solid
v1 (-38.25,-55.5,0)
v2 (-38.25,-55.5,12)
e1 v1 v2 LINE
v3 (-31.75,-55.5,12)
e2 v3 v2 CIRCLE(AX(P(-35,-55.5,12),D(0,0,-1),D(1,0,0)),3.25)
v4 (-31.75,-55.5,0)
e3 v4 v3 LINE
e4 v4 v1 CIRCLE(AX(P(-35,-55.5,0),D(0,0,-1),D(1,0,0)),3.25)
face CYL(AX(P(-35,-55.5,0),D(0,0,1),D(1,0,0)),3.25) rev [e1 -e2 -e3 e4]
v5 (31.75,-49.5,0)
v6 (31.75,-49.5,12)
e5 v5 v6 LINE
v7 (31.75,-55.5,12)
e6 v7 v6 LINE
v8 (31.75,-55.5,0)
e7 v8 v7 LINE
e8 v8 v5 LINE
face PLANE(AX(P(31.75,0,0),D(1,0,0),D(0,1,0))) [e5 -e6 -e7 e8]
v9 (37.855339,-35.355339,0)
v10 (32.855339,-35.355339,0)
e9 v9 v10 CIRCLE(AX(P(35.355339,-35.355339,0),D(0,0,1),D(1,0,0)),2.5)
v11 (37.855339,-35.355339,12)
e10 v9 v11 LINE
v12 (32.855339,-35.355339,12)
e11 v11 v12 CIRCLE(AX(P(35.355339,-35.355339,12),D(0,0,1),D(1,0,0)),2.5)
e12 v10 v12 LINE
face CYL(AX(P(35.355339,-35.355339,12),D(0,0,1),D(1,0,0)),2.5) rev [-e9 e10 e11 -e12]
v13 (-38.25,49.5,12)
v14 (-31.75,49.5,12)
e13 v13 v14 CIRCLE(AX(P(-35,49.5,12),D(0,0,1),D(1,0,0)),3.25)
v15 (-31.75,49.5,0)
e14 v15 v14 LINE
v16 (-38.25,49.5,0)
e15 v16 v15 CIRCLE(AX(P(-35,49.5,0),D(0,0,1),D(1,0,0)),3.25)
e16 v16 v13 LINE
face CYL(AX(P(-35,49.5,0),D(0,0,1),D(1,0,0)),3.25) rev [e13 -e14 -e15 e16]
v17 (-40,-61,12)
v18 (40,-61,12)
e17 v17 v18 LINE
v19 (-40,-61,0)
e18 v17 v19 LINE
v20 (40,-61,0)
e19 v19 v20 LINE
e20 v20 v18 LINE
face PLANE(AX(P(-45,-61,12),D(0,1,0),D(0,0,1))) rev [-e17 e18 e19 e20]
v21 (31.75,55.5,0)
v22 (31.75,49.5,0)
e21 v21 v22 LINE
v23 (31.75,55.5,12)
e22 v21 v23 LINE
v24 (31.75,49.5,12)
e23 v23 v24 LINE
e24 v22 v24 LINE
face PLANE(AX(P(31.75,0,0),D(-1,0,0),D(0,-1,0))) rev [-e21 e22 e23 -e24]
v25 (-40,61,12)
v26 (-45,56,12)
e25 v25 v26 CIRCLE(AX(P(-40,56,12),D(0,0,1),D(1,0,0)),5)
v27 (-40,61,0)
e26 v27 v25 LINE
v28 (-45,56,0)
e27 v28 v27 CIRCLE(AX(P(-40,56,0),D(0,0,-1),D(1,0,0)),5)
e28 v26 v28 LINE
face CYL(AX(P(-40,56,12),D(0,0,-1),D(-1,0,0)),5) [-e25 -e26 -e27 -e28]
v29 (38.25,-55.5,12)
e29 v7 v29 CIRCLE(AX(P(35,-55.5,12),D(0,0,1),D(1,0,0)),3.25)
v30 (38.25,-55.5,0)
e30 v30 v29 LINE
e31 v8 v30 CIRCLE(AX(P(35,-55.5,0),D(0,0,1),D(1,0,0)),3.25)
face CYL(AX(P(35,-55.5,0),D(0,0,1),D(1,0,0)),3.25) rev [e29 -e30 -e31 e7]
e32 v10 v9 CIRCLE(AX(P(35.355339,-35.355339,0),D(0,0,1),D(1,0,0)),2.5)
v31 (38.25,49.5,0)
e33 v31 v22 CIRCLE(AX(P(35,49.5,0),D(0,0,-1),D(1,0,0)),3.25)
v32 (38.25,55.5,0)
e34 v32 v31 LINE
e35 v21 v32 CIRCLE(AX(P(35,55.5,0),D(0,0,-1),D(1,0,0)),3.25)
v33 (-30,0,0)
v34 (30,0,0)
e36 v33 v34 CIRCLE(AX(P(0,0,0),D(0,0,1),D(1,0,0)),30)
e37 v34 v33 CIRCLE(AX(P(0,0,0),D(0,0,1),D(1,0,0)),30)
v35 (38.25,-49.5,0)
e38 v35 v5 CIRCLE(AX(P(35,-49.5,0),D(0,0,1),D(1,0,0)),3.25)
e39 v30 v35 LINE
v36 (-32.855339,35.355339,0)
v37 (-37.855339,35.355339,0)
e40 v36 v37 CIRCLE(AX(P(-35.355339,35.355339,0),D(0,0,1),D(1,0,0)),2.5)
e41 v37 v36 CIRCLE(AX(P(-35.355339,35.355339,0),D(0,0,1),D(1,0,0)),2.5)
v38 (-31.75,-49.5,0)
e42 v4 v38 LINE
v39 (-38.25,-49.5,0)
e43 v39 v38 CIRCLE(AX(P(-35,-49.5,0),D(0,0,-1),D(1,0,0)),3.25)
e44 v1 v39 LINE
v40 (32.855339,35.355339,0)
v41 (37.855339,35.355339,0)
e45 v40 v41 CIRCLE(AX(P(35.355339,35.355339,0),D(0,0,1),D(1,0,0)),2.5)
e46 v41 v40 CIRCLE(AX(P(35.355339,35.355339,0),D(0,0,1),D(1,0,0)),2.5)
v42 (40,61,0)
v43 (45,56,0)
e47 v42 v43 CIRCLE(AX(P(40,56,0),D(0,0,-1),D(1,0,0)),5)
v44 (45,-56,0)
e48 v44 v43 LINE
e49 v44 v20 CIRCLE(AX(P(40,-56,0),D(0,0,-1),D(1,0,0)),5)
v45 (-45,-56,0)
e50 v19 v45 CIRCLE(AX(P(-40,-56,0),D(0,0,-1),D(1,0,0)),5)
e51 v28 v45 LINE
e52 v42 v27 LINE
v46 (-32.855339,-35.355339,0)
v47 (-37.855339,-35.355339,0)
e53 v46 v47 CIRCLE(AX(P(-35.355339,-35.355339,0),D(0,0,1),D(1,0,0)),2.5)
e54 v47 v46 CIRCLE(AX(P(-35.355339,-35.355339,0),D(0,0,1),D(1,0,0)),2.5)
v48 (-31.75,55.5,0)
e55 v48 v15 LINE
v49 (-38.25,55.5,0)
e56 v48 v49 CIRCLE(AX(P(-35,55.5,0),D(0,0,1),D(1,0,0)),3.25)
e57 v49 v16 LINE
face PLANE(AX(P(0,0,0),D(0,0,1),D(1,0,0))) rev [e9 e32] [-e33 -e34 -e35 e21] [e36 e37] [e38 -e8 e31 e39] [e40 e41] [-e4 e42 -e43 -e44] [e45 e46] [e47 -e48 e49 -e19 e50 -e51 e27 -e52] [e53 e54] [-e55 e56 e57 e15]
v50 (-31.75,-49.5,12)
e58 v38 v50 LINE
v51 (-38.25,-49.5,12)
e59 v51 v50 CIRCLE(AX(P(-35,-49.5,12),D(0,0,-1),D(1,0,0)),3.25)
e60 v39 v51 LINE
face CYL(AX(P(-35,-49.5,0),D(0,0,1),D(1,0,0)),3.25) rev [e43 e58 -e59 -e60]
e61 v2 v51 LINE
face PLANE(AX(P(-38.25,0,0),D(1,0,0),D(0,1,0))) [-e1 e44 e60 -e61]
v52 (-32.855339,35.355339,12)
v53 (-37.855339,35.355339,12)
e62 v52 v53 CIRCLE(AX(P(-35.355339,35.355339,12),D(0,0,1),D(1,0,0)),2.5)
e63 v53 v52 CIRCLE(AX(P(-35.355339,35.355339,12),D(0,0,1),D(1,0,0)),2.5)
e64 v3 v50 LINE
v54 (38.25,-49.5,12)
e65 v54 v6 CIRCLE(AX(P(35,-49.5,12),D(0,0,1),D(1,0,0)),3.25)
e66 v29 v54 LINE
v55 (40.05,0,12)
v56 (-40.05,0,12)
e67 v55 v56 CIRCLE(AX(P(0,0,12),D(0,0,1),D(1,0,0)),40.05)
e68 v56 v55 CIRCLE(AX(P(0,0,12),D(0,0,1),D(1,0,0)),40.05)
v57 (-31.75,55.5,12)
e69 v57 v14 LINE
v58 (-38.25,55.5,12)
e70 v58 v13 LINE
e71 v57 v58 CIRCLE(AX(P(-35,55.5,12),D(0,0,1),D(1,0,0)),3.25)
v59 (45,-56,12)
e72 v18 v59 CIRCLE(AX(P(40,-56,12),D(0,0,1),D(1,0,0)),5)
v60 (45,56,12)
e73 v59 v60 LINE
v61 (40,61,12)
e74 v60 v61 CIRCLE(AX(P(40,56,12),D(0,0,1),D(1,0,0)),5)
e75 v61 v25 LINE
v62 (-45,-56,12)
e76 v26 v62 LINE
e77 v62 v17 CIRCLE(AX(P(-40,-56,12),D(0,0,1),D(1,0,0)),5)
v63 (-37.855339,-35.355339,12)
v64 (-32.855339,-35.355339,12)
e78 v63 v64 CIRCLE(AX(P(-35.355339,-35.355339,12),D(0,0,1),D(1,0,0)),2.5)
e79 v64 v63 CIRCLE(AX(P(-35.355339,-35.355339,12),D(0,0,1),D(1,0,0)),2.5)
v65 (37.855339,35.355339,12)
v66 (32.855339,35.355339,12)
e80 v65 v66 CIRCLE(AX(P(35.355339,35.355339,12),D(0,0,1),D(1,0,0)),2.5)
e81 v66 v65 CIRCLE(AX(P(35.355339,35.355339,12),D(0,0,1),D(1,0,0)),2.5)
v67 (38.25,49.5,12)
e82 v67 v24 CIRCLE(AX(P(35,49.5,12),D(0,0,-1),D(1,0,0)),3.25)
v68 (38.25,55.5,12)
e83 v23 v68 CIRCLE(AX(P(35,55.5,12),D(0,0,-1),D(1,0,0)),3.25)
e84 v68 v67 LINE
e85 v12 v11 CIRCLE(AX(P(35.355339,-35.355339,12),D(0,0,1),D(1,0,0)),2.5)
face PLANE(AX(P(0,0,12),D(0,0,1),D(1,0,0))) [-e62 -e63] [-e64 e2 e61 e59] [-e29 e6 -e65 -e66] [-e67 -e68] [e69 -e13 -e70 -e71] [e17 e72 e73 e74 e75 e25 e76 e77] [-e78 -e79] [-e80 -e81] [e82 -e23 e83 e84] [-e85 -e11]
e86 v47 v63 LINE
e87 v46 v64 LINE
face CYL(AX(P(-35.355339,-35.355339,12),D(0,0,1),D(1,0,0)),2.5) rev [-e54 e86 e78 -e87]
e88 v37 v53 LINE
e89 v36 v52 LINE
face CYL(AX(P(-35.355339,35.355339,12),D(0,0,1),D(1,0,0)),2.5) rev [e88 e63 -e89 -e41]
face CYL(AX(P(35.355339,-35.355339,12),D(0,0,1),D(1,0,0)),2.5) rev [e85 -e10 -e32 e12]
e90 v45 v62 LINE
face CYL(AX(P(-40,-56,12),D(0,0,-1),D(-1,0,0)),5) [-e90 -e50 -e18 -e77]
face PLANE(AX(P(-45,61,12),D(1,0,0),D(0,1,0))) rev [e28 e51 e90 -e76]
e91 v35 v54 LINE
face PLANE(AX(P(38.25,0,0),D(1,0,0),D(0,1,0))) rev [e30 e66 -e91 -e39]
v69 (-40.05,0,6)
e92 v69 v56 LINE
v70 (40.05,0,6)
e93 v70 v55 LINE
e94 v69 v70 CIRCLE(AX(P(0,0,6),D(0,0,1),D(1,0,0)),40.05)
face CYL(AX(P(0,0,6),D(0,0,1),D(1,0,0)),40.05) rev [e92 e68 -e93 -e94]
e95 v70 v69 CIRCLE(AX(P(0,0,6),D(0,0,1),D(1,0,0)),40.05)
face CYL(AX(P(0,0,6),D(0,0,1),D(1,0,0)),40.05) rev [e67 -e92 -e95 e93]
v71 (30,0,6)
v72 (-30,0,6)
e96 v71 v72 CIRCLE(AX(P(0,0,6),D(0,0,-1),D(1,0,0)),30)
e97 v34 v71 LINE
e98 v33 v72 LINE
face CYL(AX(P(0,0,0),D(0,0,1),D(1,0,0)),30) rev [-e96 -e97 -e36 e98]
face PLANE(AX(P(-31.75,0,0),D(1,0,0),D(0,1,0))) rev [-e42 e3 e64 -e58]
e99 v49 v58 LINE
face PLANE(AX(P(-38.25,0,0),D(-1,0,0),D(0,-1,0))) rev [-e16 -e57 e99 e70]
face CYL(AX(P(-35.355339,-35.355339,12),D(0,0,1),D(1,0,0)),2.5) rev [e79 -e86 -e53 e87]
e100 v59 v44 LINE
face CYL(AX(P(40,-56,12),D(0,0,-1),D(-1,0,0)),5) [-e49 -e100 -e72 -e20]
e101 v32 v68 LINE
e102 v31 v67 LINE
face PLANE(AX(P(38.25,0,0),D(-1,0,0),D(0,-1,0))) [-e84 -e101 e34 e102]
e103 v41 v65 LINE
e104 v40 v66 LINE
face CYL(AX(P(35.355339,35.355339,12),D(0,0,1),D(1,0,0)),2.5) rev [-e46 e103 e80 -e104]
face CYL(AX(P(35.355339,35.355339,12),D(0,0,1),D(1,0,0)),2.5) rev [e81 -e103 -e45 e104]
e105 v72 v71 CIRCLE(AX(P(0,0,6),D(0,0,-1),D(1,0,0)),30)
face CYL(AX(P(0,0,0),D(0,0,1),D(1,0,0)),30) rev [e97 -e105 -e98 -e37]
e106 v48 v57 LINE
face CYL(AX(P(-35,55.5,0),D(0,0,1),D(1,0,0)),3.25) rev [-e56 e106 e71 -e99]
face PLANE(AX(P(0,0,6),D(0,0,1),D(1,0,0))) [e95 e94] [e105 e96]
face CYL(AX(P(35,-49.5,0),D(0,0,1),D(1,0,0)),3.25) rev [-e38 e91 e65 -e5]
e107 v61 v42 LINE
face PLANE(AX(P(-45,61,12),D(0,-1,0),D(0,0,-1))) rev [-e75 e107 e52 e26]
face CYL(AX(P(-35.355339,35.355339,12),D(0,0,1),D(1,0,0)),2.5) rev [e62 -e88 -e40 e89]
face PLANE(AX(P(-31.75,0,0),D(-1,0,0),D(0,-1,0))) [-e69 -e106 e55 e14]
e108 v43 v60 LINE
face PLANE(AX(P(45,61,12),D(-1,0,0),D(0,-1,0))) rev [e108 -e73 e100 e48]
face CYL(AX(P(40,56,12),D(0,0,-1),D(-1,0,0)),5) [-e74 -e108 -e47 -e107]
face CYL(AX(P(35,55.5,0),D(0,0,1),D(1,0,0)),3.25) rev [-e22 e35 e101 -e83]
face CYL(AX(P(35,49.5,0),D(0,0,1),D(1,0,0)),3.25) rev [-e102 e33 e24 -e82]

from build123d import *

# Parameters (mm, degrees)
SKETCH1_W           = 90
SKETCH1_H           = 122
BOSS_EXTRUDE1_DEPTH = 12
SKETCH2_R           = 30
CUT_EXTRUDE1_DEPTH  = 77.746335417
SKETCH3_R           = 40.05
CUT_EXTRUDE2_DEPTH  = 6
M6_TAPPED_HOLE1_D   = 5
CUT_EXTRUDE3_DEPTH  = 77.746335417
FILLET1_R           = 5


with BuildPart() as part:
    # Sketch1 → Boss-Extrude1 (new body)
    with BuildSketch(Plane.XY):
        Rectangle(SKETCH1_W, SKETCH1_H)
    extrude(amount=BOSS_EXTRUDE1_DEPTH)

    # Sketch2 → Cut-Extrude1 (cut, through all)
    with BuildSketch(Plane.XY.offset(12)):
        Circle(SKETCH2_R)
    extrude(amount=-CUT_EXTRUDE1_DEPTH, mode=Mode.SUBTRACT)

    # Sketch3 → Cut-Extrude2 (cut)
    with BuildSketch(Plane.XY.offset(12)):
        Circle(SKETCH3_R)
    extrude(amount=-CUT_EXTRUDE2_DEPTH, mode=Mode.SUBTRACT)

    # M6 Tapped Hole1 (through all)
    with Locations(Plane.XY.offset(12)):
        with Locations((35.355339059, 35.355339059), (-35.355339059, 35.355339059), (-35.355339059, -35.355339059), (35.355339059, -35.355339059)):
            Hole(M6_TAPPED_HOLE1_D / 2)

    # Sketch6 → Cut-Extrude3 (cut, through all)
    with BuildSketch(Plane.XY.offset(12)):
        with BuildLine():
            Line((-38.25, 55.5), (-38.25, 49.5))
            ThreePointArc((-38.25, 49.5), (-35, 46.25), (-31.75, 49.5))
            Line((-31.75, 49.5), (-31.75, 55.5))
            ThreePointArc((-31.75, 55.5), (-35, 58.75), (-38.25, 55.5))
        make_face()
        with BuildLine():
            ThreePointArc((38.25, 49.5), (35, 46.25), (31.75, 49.5))
            Line((31.75, 49.5), (31.75, 55.5))
            ThreePointArc((31.75, 55.5), (35, 58.75), (38.25, 55.5))
            Line((38.25, 55.5), (38.25, 49.5))
        make_face()
        with BuildLine():
            Line((38.25, -55.5), (38.25, -49.5))
            ThreePointArc((38.25, -49.5), (35, -46.25), (31.75, -49.5))
            Line((31.75, -49.5), (31.75, -55.5))
            ThreePointArc((31.75, -55.5), (35, -58.75), (38.25, -55.5))
        make_face()
        with BuildLine():
            ThreePointArc((-38.25, -49.5), (-35, -46.25), (-31.75, -49.5))
            Line((-31.75, -49.5), (-31.75, -55.5))
            ThreePointArc((-31.75, -55.5), (-35, -58.75), (-38.25, -55.5))
            Line((-38.25, -55.5), (-38.25, -49.5))
        make_face()
    extrude(amount=-CUT_EXTRUDE3_DEPTH, mode=Mode.SUBTRACT)

    # Fillet1
    fillet1_edges = [part.edges().sort_by_distance(p)[0] for p in [
        (45, -61, 6),
        (-45, -61, 6),
        (-45, 61, 6),
        (45, 61, 6),
    ]]
    fillet(fillet1_edges, radius=FILLET1_R)


solid = part.part
